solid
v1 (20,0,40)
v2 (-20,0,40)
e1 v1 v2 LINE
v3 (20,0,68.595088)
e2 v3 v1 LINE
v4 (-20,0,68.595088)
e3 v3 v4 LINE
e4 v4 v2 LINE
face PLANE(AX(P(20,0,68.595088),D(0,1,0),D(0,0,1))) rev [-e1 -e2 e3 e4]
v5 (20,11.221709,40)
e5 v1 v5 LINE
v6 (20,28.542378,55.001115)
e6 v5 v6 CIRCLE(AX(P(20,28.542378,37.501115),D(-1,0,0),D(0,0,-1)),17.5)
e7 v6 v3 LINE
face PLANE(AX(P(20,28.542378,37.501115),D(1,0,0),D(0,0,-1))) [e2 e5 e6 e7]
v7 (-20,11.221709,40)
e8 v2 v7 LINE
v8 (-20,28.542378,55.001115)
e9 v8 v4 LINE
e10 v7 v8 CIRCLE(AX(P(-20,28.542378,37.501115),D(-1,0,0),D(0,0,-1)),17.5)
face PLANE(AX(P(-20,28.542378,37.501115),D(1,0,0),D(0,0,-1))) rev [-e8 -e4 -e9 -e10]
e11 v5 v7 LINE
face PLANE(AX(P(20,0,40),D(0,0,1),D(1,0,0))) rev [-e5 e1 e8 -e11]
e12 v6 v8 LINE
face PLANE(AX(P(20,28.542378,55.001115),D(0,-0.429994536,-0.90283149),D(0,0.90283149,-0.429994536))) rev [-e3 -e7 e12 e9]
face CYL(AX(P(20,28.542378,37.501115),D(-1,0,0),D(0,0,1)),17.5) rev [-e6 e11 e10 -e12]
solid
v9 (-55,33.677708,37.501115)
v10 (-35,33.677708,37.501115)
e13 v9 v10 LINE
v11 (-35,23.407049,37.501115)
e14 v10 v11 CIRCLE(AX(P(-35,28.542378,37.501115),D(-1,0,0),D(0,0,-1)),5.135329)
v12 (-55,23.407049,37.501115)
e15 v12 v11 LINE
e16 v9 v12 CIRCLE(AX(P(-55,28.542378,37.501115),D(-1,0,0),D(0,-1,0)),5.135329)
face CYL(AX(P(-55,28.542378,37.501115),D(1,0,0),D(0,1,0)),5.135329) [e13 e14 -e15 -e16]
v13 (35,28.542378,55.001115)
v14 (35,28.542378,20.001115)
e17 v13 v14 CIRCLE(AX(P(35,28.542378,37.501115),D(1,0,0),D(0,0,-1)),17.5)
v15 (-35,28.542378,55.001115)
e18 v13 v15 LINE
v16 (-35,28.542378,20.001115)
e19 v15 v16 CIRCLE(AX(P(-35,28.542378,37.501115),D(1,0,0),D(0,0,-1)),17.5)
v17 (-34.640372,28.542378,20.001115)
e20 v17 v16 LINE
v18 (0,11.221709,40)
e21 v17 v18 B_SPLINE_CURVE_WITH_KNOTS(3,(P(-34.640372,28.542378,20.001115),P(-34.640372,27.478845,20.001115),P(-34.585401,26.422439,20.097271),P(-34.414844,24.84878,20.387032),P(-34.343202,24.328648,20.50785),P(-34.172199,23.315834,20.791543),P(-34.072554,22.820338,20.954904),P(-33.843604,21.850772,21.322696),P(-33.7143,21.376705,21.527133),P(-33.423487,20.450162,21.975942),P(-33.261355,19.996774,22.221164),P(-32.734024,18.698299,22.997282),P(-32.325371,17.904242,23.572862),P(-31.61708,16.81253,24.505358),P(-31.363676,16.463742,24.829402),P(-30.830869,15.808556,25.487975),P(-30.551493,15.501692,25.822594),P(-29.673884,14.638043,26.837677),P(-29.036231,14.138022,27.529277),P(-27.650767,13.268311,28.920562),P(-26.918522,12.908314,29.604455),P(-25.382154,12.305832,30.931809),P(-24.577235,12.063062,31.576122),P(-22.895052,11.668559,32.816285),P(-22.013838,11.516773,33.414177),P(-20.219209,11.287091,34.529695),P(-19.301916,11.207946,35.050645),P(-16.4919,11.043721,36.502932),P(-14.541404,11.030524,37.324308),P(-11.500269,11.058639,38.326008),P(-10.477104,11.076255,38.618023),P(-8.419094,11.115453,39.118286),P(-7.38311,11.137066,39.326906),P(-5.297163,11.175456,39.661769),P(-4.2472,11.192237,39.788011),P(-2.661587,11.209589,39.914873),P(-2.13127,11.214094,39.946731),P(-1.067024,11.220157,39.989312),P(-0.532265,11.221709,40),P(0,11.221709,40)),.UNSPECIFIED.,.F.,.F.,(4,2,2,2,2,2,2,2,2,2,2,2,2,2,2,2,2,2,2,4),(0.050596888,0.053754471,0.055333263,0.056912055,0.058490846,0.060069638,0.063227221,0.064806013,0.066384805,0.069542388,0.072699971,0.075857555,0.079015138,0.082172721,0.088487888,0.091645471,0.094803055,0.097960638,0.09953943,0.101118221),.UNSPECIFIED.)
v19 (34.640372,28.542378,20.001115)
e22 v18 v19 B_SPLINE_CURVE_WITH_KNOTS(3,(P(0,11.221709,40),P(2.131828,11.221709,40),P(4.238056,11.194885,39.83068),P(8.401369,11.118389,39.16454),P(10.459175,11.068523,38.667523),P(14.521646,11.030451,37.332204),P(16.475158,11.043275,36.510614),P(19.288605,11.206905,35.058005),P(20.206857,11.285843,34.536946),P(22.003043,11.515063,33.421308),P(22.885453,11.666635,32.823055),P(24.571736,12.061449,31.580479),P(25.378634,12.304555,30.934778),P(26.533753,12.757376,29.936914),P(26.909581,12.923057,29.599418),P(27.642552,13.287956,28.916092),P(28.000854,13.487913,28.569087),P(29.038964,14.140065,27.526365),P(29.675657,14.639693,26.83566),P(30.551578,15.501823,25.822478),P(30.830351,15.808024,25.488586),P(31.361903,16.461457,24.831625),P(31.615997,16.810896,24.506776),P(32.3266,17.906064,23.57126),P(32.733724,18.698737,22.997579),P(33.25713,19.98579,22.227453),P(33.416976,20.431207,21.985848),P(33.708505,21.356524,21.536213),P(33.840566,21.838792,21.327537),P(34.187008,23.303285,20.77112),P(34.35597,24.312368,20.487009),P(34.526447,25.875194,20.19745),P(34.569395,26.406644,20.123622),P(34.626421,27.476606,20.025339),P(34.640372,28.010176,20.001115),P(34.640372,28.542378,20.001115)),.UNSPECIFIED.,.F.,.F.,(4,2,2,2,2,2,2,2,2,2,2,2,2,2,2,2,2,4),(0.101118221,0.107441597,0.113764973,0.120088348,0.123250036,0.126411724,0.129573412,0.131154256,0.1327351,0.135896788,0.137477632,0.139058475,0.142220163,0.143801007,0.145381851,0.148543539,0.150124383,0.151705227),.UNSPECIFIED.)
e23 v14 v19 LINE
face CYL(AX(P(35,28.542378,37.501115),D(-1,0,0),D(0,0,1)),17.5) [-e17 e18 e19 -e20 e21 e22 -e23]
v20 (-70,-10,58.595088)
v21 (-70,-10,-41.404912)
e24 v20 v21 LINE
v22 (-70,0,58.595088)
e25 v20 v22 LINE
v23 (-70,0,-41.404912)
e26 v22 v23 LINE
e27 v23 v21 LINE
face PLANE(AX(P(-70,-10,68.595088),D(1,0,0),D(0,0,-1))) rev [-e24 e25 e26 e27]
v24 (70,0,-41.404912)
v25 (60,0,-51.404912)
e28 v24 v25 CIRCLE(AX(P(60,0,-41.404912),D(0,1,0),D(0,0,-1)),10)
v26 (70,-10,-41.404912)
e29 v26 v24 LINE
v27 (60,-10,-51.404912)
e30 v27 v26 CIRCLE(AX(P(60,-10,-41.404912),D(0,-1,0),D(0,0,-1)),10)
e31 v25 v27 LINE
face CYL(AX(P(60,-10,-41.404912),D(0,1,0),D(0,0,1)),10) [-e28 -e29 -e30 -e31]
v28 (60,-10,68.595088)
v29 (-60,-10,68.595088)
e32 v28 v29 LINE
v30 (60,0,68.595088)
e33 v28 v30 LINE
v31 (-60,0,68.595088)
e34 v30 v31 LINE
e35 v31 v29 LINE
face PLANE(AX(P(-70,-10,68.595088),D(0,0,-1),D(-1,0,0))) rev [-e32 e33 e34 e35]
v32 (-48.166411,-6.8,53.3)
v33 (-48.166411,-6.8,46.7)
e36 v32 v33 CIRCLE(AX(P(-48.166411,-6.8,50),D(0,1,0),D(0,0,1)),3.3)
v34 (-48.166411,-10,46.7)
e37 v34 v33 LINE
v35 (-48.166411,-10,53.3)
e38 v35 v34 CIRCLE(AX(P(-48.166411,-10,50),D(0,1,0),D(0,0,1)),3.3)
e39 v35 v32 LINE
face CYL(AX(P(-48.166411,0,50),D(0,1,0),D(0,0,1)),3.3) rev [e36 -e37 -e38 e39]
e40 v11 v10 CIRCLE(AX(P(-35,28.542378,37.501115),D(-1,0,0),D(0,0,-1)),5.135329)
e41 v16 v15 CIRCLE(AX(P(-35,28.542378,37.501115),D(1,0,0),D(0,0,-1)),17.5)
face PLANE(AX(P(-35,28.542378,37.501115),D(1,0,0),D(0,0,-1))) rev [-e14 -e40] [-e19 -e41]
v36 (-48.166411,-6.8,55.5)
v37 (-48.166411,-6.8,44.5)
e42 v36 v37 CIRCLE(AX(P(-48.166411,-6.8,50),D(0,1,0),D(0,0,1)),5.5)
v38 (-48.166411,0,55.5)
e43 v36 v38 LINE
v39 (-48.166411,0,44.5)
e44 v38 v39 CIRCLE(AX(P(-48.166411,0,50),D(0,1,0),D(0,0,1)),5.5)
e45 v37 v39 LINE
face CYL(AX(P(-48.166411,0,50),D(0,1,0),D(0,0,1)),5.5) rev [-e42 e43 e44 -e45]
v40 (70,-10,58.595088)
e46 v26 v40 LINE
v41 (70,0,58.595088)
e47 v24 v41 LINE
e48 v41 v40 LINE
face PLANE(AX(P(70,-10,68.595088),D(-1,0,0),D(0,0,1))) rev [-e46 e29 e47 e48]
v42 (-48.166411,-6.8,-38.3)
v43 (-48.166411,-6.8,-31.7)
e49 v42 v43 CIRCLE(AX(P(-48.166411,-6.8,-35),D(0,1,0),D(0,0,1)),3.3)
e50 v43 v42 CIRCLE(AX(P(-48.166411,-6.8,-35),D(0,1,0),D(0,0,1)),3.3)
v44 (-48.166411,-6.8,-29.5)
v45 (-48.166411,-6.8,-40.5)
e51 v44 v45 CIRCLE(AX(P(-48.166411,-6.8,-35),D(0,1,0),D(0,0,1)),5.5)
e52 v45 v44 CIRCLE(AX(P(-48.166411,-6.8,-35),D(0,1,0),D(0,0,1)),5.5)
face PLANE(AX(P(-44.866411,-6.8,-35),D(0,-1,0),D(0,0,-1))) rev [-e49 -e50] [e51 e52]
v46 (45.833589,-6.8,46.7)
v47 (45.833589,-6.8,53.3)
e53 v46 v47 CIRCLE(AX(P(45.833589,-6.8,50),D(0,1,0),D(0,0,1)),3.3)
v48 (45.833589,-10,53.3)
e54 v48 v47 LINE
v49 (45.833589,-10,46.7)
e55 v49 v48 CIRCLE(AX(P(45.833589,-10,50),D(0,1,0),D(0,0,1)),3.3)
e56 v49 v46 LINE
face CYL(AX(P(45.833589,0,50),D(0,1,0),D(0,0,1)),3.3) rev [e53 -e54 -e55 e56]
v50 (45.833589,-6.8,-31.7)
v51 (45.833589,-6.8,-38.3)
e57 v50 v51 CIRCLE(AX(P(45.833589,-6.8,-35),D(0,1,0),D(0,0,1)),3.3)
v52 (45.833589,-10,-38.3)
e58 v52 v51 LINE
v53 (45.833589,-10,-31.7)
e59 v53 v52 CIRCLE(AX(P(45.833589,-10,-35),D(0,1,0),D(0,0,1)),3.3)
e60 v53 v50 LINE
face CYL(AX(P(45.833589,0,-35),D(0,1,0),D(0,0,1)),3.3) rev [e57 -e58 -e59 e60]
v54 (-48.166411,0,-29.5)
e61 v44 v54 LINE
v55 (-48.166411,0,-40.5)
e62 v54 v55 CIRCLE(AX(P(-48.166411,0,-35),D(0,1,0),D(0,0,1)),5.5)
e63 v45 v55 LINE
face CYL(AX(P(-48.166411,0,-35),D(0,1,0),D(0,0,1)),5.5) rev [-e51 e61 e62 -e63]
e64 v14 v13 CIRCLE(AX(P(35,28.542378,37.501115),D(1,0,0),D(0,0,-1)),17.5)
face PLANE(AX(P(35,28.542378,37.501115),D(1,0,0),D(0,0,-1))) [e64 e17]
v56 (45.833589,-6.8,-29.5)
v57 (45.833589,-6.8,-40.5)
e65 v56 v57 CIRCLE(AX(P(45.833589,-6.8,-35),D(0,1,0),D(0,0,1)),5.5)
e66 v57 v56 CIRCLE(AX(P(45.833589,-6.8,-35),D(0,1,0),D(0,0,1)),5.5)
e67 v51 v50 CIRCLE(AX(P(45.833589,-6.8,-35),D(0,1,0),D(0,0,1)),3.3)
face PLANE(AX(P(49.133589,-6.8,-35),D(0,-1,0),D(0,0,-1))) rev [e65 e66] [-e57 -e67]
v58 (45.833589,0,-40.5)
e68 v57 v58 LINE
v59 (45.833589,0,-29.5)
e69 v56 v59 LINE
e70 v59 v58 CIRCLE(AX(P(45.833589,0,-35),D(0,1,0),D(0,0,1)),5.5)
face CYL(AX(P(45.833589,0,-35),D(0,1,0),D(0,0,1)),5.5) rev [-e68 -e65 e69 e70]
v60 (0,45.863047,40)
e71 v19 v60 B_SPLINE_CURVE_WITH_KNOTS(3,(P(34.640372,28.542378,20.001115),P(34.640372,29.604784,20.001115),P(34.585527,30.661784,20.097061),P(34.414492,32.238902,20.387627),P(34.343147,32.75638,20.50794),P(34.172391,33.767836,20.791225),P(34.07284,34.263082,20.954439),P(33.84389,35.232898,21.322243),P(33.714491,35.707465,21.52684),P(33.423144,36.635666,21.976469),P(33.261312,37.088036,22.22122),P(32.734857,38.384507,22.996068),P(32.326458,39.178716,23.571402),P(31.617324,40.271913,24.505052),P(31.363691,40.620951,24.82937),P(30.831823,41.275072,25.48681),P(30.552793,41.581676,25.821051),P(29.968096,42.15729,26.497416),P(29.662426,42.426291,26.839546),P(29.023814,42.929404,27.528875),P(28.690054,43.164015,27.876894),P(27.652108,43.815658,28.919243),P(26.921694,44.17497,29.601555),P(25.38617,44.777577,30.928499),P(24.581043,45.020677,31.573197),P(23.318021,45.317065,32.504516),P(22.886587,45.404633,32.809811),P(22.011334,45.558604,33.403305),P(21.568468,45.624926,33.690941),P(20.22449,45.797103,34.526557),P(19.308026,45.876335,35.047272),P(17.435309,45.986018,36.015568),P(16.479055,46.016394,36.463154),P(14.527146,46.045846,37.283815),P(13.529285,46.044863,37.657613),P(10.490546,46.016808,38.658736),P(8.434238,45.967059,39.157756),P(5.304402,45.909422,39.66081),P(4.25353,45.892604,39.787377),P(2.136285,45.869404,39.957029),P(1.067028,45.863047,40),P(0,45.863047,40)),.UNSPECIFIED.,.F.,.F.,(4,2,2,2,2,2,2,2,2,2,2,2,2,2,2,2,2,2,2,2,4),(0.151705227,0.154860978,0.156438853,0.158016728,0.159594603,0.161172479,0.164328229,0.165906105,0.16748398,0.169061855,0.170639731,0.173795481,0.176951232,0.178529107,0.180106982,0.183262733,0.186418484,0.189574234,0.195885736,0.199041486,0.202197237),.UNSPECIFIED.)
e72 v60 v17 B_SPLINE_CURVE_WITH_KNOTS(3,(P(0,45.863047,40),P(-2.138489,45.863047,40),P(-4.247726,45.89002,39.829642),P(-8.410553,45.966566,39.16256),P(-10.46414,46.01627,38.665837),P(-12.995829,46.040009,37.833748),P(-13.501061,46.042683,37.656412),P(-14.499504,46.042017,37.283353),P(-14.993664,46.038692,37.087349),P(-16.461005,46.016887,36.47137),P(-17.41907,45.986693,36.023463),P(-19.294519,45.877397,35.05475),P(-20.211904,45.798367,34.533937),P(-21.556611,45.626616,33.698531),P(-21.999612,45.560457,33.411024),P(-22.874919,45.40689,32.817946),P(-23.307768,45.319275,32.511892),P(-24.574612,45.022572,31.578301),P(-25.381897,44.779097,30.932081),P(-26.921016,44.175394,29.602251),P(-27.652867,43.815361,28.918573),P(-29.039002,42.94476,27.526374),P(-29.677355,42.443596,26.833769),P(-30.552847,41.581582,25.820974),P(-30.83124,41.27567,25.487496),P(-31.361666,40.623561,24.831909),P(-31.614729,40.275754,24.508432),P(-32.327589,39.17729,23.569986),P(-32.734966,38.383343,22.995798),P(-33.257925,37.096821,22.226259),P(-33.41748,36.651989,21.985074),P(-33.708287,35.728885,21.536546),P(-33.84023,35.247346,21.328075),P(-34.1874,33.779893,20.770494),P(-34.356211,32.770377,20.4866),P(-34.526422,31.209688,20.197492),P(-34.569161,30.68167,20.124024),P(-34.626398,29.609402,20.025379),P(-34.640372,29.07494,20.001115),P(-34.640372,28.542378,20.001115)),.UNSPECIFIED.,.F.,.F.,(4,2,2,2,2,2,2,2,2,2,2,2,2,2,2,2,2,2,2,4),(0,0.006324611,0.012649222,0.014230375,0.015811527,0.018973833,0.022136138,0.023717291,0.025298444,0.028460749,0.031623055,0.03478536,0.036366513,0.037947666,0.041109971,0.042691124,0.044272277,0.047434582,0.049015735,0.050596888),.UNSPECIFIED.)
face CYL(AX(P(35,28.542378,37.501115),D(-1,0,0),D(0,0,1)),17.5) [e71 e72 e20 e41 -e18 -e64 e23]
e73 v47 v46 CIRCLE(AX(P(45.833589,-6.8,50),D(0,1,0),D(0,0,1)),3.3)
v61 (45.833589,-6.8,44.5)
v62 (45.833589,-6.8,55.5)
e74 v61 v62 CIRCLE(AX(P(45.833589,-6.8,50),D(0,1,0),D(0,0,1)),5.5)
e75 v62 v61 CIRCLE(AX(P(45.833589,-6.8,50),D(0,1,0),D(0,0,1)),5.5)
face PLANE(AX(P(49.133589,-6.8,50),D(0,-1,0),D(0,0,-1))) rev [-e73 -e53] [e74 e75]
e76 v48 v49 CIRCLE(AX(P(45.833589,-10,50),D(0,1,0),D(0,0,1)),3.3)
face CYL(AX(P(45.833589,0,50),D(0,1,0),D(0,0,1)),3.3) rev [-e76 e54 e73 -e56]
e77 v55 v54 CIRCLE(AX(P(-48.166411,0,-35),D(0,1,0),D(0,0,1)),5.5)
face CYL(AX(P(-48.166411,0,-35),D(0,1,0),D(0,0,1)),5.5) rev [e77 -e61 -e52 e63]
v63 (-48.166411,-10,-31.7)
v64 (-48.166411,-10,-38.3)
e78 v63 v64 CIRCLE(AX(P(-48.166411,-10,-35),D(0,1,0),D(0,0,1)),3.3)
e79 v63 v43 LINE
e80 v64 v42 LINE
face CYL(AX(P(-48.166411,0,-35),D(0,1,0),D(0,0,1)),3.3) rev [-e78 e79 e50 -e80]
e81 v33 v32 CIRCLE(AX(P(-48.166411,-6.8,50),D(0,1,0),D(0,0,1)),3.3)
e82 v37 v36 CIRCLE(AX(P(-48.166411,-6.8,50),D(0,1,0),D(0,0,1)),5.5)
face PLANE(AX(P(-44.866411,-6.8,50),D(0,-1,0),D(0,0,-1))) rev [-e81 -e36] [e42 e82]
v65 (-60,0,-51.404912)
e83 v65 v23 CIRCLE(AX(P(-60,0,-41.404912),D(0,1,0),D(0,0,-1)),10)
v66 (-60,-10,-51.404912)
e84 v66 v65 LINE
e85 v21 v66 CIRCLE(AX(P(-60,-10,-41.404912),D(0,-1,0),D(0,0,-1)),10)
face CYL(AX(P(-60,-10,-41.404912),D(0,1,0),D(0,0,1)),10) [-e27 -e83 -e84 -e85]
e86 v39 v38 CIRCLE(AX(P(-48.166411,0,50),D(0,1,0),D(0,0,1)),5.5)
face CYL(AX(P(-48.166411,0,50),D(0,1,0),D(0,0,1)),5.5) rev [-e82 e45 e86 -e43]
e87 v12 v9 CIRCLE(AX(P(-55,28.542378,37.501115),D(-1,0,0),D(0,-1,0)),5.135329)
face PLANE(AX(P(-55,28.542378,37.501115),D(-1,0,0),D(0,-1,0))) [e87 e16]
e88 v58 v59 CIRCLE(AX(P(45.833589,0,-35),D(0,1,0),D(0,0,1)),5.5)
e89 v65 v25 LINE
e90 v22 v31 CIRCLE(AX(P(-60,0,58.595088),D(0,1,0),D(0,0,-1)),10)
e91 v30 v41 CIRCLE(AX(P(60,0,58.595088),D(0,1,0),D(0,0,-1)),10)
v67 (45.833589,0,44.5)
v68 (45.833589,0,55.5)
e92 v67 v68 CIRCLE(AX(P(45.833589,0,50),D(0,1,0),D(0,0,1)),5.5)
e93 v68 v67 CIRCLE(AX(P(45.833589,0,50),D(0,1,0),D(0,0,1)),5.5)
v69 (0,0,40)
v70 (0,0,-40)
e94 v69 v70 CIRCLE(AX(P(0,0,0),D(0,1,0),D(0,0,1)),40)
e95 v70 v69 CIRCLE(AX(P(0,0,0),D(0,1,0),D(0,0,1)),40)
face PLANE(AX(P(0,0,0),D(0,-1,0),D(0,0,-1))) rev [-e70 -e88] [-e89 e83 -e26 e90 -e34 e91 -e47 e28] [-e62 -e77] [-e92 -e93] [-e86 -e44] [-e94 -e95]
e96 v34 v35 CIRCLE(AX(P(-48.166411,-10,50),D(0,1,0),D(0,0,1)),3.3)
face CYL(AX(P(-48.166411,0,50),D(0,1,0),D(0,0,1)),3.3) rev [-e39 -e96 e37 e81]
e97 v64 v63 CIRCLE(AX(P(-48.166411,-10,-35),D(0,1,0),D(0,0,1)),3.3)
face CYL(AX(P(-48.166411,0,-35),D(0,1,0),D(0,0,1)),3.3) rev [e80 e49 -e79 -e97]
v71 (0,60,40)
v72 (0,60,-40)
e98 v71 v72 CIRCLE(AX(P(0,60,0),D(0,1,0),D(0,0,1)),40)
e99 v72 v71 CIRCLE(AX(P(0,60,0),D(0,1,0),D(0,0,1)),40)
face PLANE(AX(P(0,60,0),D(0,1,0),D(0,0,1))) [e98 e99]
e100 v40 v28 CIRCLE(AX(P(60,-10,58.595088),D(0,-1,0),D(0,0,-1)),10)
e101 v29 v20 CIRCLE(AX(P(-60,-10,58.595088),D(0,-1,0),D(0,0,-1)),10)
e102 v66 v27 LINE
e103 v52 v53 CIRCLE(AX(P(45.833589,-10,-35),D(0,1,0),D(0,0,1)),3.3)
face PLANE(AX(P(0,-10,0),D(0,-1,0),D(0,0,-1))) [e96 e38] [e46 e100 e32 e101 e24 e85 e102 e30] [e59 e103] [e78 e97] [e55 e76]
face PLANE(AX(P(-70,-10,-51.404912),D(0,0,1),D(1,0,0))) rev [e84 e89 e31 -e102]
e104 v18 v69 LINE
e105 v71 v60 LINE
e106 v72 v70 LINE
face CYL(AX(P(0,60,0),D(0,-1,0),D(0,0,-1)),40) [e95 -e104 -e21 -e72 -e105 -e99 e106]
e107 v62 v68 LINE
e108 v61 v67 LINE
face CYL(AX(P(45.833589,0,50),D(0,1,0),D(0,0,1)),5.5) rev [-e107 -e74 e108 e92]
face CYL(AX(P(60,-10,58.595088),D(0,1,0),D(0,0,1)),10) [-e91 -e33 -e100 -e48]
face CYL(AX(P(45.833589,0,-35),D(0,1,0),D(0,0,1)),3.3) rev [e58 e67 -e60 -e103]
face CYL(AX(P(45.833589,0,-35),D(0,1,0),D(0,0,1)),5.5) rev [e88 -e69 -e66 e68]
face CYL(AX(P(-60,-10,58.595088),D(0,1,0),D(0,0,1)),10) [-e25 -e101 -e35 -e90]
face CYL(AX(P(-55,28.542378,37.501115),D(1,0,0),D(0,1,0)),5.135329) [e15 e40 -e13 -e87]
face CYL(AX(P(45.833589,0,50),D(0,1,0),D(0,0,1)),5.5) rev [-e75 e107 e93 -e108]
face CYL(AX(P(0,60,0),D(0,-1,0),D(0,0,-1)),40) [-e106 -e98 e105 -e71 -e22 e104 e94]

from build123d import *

# Parameters (mm, degrees)
SKETCH1_R                                   = 40
BOSS_EXTRUDE1_DEPTH                         = 60
SKETCH2_W                                   = 140
SKETCH2_H                                   = 120
BOSS_EXTRUDE2_DEPTH                         = 10
SKETCH3_R                                   = 17.5
BOSS_EXTRUDE3_DEPTH                         = 35
BOSS_EXTRUDE6_DEPTH                         = 20
FILLET1_R                                   = 10
HOLE_SIZE_PER_SOCKET_HEAD_CAP_SCREW_2_COUNT = 2
HOLE_SIZE_PER_SOCKET_HEAD_CAP_SCREW_2_PITCH = 85
HOLE_SIZE_PER_SOCKET_HEAD_CAP_SCREW_3_COUNT = 2
HOLE_SIZE_PER_SOCKET_HEAD_CAP_SCREW_3_PITCH = 126.732000694
HOLE_SIZE_PER_SOCKET_HEAD_CAP_SCREW_4_COUNT = 2
HOLE_SIZE_PER_SOCKET_HEAD_CAP_SCREW_4_PITCH = 94
SKETCH10_R                                  = 5.135329367
BOSS_EXTRUDE7_DEPTH                         = 20


with BuildPart() as part:
    # Sketch1 → Boss-Extrude1 (new body)
    with BuildSketch(Plane(origin=(0, 0, 0), x_dir=(1, 0, 0), z_dir=(0, 1, 0))):
        with Locations(Location((0, 0, 0), (0, 0, 270))):
            Circle(SKETCH1_R)
    extrude(amount=BOSS_EXTRUDE1_DEPTH)

    # Sketch2 → Boss-Extrude2 (add)
    with BuildSketch(Plane.XZ):
        with Locations((0, 8.595087693)):
            Rectangle(SKETCH2_W, SKETCH2_H)
    extrude(amount=BOSS_EXTRUDE2_DEPTH)

    # Sketch3 → Boss-Extrude3 (add, symmetric)
    with BuildSketch(Plane(origin=(0, 0, 0), x_dir=(0, 0, -1), z_dir=(1, 0, 0))):
        with Locations((-37.50111495, 28.542378204)):
            Circle(SKETCH3_R)
    extrude(amount=BOSS_EXTRUDE3_DEPTH, both=True)

    # Fillet1
    fillet1_edges = [part.edges().sort_by_distance(p)[0] for p in [
        (70, -5, -51.404912307),
        (70, -5, 68.595087693),
        (-70, -5, 68.595087693),
        (-70, -5, -51.404912307),
    ]]
    fillet(fillet1_edges, radius=FILLET1_R)

    # Sketch9 → Hole size per socket head cap screw type1 (revolve, cut)
    with BuildSketch(Plane(origin=(-48.166410727, 0, 50), x_dir=(0, 0, 1), z_dir=(1, 0, 0))):
        Polygon((0, 0), (0, 10), (3.3, 10), (3.3, 6.8), (5.5, 6.8), (5.5, 0), align=None)
    hole_size_per_socket_head_cap_screw_type = revolve(axis=Axis((-48.166410727, 6.35, 50), (0, -1, 0)), mode=Mode.SUBTRACT)

    # Hole size per socket head cap screw  2: Hole size per socket head cap screw type1 ×2
    with Locations(*[(0, 0, -i * HOLE_SIZE_PER_SOCKET_HEAD_CAP_SCREW_2_PITCH) for i in range(1, HOLE_SIZE_PER_SOCKET_HEAD_CAP_SCREW_2_COUNT)]):
        add(hole_size_per_socket_head_cap_screw_type, mode=Mode.SUBTRACT)

    # Hole size per socket head cap screw  3: Hole size per socket head cap screw type1 ×2
    with Locations(*[Vector(0.741722686337812, 0, -0.6707066844544043) * (i * HOLE_SIZE_PER_SOCKET_HEAD_CAP_SCREW_3_PITCH) for i in range(1, HOLE_SIZE_PER_SOCKET_HEAD_CAP_SCREW_3_COUNT)]):
        add(hole_size_per_socket_head_cap_screw_type, mode=Mode.SUBTRACT)

    # Hole size per socket head cap screw  4: Hole size per socket head cap screw type1 ×2
    with Locations(*[(i * HOLE_SIZE_PER_SOCKET_HEAD_CAP_SCREW_4_PITCH, 0, 0) for i in range(1, HOLE_SIZE_PER_SOCKET_HEAD_CAP_SCREW_4_COUNT)]):
        add(hole_size_per_socket_head_cap_screw_type, mode=Mode.SUBTRACT)

    # Sketch10 → Boss-Extrude7 (add)
    with BuildSketch(Plane.ZY.offset(35)):
        with Locations(Location((37.50111495, 28.542378204, 0), (0, 0, 180))):
            Circle(SKETCH10_R)
    extrude(amount=BOSS_EXTRUDE7_DEPTH)


with BuildPart() as body_2:
    # Sketch4 → Boss-Extrude6 (new, symmetric)
    with BuildSketch(Plane(origin=(0, 0, 0), x_dir=(0, 0, -1), z_dir=(1, 0, 0))):
        with BuildLine():
            Line((-55.00111495, 28.542378204), (-68.595087693, 0))
            Line((-68.595087693, 0), (-40, 0))
            Line((-40, 0), (-40, 11.221709236))
            ThreePointArc((-40, 11.221709236), (-50.729502765, 17.085513196), (-55.00111495, 28.542378204))
        make_face()
    extrude(amount=BOSS_EXTRUDE6_DEPTH, both=True)


solid = Compound([part.part, body_2.part])
